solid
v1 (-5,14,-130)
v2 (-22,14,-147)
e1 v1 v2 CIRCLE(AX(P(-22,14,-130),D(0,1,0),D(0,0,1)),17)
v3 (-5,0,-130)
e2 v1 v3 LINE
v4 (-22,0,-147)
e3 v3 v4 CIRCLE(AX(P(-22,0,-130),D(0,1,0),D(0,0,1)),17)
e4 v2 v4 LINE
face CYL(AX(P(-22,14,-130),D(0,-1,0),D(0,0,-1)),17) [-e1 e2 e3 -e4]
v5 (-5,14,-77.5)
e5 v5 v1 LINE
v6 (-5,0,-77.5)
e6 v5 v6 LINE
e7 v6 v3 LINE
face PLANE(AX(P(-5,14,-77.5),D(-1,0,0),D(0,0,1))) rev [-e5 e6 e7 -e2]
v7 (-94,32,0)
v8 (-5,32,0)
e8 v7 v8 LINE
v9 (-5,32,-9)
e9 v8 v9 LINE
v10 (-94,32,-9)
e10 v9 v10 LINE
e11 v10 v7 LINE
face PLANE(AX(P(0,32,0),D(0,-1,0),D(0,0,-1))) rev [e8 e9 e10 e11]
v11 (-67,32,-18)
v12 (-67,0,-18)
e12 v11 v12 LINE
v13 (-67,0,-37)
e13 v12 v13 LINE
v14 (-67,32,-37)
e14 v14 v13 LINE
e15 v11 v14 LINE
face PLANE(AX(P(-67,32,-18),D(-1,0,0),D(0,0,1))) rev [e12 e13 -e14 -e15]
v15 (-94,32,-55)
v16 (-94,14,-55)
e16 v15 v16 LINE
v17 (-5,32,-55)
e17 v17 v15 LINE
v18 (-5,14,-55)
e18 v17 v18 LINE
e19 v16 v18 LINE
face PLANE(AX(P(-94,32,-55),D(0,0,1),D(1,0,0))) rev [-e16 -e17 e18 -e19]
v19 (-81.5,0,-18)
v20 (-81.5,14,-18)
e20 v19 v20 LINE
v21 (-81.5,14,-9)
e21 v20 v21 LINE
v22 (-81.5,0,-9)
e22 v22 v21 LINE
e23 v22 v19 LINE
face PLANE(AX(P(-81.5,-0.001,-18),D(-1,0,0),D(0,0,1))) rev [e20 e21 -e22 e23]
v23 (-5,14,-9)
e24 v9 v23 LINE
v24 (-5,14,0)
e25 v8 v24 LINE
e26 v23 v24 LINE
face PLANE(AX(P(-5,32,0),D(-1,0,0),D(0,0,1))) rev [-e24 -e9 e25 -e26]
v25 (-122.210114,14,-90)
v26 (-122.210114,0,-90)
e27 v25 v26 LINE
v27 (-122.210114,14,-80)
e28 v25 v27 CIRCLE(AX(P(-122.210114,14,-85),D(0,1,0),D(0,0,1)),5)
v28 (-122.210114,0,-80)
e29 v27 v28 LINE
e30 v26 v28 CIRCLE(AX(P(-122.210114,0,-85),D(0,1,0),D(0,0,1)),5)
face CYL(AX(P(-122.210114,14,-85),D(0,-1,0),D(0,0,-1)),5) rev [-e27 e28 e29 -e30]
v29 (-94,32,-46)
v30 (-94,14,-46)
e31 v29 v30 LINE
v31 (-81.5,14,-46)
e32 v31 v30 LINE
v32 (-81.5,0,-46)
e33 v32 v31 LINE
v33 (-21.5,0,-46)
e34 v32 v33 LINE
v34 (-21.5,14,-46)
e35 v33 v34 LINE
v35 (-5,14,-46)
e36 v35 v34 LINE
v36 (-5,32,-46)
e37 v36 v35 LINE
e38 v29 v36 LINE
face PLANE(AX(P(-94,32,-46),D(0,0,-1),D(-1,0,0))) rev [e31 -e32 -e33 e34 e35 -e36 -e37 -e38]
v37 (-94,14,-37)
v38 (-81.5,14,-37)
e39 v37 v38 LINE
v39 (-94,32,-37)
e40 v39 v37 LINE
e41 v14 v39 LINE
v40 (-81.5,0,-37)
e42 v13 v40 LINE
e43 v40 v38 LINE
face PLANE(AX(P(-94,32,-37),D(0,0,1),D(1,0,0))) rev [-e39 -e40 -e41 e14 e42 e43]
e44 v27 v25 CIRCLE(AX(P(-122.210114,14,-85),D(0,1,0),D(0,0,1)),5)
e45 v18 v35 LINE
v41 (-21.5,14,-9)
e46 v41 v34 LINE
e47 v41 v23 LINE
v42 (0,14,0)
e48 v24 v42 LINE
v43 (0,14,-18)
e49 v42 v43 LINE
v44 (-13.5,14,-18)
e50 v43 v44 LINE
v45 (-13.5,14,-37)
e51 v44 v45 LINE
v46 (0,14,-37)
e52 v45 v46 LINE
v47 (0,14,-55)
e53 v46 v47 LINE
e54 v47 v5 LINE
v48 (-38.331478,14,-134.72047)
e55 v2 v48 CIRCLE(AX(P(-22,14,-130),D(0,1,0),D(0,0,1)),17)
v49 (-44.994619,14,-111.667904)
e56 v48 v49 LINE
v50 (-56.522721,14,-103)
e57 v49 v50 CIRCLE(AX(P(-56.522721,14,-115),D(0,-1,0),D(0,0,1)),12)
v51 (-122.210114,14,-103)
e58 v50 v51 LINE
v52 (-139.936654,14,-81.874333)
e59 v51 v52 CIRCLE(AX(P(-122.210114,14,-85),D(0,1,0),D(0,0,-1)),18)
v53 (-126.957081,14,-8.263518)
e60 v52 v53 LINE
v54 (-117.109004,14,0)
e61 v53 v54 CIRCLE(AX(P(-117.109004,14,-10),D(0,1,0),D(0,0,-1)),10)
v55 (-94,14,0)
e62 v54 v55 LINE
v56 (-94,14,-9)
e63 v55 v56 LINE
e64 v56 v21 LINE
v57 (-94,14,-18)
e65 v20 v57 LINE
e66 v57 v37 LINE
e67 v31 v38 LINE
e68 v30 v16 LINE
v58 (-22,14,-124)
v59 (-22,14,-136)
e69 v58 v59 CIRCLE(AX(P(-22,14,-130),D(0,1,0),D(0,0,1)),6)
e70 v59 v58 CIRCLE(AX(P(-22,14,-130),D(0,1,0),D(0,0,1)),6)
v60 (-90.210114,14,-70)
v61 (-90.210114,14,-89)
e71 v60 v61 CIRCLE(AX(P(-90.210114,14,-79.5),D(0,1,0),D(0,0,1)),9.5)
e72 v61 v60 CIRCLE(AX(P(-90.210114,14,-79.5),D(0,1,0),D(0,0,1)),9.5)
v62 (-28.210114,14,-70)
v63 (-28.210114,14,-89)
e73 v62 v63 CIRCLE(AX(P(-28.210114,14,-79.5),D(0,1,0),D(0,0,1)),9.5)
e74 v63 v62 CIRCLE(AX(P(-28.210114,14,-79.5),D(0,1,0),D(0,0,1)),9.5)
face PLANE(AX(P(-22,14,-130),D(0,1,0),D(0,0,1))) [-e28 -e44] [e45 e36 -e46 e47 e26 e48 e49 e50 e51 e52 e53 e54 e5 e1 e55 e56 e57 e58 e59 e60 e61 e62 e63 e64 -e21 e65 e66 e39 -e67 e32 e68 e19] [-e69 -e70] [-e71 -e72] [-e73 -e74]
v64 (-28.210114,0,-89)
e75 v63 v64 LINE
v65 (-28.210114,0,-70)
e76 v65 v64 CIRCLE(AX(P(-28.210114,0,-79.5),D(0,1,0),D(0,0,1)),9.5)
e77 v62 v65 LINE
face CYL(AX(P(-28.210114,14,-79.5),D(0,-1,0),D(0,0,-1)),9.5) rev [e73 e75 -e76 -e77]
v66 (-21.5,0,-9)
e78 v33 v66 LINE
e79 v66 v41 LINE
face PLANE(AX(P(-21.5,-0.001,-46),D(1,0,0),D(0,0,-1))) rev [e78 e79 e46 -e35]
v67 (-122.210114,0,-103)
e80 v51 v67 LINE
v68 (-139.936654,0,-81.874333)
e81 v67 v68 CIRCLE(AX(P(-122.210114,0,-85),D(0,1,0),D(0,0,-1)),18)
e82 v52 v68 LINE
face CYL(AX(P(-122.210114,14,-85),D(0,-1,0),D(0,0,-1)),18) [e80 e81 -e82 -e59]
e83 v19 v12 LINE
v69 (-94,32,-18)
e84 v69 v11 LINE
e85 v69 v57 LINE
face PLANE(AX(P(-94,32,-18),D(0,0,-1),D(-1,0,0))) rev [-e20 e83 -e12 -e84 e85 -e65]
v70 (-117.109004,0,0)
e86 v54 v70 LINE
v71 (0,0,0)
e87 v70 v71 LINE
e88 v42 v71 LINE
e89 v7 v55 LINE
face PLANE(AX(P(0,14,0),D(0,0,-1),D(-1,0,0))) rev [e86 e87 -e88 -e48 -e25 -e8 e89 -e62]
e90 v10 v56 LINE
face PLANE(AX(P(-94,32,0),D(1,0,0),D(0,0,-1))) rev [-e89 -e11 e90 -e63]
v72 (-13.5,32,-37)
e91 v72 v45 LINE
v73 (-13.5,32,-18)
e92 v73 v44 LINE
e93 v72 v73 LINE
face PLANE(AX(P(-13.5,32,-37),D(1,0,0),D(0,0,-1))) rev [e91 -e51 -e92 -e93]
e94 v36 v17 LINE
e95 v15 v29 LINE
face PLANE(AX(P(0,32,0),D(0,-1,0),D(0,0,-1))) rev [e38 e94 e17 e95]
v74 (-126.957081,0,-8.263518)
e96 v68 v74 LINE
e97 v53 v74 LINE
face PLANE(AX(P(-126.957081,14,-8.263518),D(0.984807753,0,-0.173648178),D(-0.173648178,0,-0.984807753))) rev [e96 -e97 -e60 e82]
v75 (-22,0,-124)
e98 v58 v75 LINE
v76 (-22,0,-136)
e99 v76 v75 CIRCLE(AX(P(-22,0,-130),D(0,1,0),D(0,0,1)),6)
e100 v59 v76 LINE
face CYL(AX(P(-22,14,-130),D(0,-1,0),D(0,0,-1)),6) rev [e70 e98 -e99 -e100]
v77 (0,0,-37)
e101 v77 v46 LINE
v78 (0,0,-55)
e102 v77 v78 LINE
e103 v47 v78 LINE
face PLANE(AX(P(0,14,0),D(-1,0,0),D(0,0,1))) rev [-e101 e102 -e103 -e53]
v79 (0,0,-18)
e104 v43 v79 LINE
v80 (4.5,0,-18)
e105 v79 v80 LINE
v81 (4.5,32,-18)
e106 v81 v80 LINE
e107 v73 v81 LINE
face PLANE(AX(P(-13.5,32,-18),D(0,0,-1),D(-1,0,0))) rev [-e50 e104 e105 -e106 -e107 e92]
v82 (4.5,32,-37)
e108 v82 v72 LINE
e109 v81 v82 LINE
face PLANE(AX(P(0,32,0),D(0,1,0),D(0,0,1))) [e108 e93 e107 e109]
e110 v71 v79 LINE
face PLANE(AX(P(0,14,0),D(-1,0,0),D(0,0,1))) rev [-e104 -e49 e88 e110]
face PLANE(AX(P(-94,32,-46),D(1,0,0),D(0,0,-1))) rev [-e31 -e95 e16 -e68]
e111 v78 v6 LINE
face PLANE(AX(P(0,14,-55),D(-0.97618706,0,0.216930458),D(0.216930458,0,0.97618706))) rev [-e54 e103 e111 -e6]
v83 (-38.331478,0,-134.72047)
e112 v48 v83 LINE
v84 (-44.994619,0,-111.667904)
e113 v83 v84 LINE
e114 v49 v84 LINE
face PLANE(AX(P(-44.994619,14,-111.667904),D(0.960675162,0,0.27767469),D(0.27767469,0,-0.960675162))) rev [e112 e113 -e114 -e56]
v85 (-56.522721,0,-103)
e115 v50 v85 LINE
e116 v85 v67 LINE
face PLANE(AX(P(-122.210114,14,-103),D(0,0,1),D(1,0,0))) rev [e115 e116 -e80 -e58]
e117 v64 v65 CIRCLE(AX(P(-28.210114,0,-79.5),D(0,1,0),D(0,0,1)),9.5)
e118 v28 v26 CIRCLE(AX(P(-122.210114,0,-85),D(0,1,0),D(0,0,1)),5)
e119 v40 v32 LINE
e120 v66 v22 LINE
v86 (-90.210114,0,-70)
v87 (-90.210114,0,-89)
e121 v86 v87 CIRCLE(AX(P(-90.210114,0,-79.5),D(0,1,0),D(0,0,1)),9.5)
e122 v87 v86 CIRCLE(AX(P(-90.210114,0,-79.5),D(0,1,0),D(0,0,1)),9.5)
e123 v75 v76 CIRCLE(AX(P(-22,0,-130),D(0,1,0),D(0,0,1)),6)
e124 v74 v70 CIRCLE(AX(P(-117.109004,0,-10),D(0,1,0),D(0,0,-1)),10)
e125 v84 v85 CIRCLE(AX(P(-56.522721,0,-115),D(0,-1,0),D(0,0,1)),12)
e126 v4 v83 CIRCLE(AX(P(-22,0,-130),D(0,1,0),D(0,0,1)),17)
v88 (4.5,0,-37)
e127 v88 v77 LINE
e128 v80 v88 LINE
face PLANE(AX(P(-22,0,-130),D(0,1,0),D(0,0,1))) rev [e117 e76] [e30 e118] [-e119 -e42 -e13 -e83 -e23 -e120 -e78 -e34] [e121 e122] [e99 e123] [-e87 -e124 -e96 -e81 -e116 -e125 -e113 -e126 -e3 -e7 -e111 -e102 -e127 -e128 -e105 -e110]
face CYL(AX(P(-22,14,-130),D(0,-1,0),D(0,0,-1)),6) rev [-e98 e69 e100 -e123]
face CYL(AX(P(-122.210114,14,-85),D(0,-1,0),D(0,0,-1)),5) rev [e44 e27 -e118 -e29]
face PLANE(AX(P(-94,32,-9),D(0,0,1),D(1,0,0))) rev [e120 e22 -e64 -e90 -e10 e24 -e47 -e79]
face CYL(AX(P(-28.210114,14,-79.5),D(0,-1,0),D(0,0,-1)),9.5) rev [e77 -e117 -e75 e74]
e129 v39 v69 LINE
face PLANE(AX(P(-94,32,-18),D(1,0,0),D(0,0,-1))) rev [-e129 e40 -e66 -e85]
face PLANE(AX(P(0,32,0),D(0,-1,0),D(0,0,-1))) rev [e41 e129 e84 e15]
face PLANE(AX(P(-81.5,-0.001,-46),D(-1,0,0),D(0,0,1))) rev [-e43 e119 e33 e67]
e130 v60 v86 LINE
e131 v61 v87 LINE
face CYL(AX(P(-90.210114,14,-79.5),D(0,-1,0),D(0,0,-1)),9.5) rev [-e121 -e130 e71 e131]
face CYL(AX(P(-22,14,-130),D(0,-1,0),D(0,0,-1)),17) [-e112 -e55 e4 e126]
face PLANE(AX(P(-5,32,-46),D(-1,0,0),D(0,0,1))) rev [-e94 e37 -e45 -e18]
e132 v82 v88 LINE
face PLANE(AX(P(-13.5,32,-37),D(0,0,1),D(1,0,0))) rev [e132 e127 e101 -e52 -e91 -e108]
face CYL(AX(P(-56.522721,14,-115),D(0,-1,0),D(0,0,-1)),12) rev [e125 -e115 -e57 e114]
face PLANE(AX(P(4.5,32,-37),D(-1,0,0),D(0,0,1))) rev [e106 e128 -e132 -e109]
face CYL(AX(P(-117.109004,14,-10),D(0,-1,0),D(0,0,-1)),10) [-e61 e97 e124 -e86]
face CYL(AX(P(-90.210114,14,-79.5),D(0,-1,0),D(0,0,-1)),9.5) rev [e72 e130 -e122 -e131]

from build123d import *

# Parameters (mm, degrees)
BASE_PLATE_PROFILE_SKETCH_R   = 6
BASE_PLATE_PROFILE_SKETCH_R_2 = 5
BASE_PLATE_PROFILE_SKETCH_R_3 = 9.5
BASE_PLATE_14MM_DEPTH         = 14
INTERLOCKING_RAILS_SKETCH_W   = 89
INTERLOCKING_RAILS_SKETCH_H   = 9
INTERLOCKING_RAILS_SKETCH_W_2 = 27
INTERLOCKING_RAILS_SKETCH_H_2 = 19
INTERLOCKING_RAILS_SKETCH_W_3 = 18
INTERLOCKING_RAILS_32MM_DEPTH = 32
RAIL_SLOT_CUT_REACH           = 205.941


with BuildPart() as part:
    # Base Plate Profile Sketch → Base Plate 14mm (new body)
    with BuildSketch(Plane(origin=(0, 0, 0), x_dir=(1, 0, 0), z_dir=(0, 1, 0))):
        with BuildLine():
            Line((0, 0), (-117.109003688, 0))
            ThreePointArc((-117.109003688, 0), (-123.536879785, 2.339555569), (-126.957081218, 8.263518223))
            Line((-126.957081218, 8.263518223), (-139.9366539, 81.874332802))
            ThreePointArc((-139.9366539, 81.874332802), (-135.998914322, 96.570176974), (-122.210114346, 103))
            Line((-122.210114346, 103), (-56.522720755, 103))
            ThreePointArc((-56.522720755, 103), (-49.311103576, 105.408723877), (-44.994618812, 111.667903721))
            Line((-44.994618812, 111.667903721), (-38.331477751, 134.720469728))
            ThreePointArc((-38.331477751, 134.720469728), (-19.616213283, 146.832039713), (-5, 130))
            Line((-5, 130), (-5, 77.5))
            Line((-5, 77.5), (0, 55))
            Line((0, 55), (0, 0))
        make_face()
        with Locations(Location((-22, 130, 0), (0, 0, 270))):
            Circle(BASE_PLATE_PROFILE_SKETCH_R, mode=Mode.SUBTRACT)
        with Locations(Location((-122.210114346, 85, 0), (0, 0, 270))):
            Circle(BASE_PLATE_PROFILE_SKETCH_R_2, mode=Mode.SUBTRACT)
        with Locations(Location((-90.210114346, 79.5, 0), (0, 0, 270))):
            Circle(BASE_PLATE_PROFILE_SKETCH_R_3, mode=Mode.SUBTRACT)
        with Locations(Location((-28.210114346, 79.5, 0), (0, 0, 270))):
            Circle(BASE_PLATE_PROFILE_SKETCH_R_3, mode=Mode.SUBTRACT)
    extrude(amount=BASE_PLATE_14MM_DEPTH)

    # Interlocking Rails Sketch → Interlocking Rails 32mm (add)
    with BuildSketch(Plane(origin=(0, 0, 0), x_dir=(1, 0, 0), z_dir=(0, 1, 0))):
        with Locations((-49.5, 4.5)):
            Rectangle(INTERLOCKING_RAILS_SKETCH_W, INTERLOCKING_RAILS_SKETCH_H)
        with Locations((-80.5, 27.5)):
            Rectangle(INTERLOCKING_RAILS_SKETCH_W_2, INTERLOCKING_RAILS_SKETCH_H_2)
        with Locations((-49.5, 50.5)):
            Rectangle(INTERLOCKING_RAILS_SKETCH_W, INTERLOCKING_RAILS_SKETCH_H)
        with Locations((-4.5, 27.5)):
            Rectangle(INTERLOCKING_RAILS_SKETCH_W_3, INTERLOCKING_RAILS_SKETCH_H_2)
    extrude(amount=INTERLOCKING_RAILS_32MM_DEPTH)

    # Rail Slot Sketch → Rail Slot Cut (cut, up to next)
    with BuildSketch(Plane(origin=(0, 14, 0), x_dir=(1, 0, 0), z_dir=(0, 1, 0)), mode=Mode.PRIVATE) as rail_slot_cut_sk1:
        Polygon((-81.5, 46), (-81.5, 37), (-67, 37), (-67, 18), (-81.5, 18), (-81.5, 9), (-21.5, 9), (-21.5, 46), align=None)
    rail_slot_cut_tool1 = extrude(rail_slot_cut_sk1.sketch, amount=-RAIL_SLOT_CUT_REACH, mode=Mode.PRIVATE) & part.part
    add(rail_slot_cut_tool1.solids().sort_by_distance((-48.276742, 14, -27.5))[0], mode=Mode.SUBTRACT)


solid = part.part
